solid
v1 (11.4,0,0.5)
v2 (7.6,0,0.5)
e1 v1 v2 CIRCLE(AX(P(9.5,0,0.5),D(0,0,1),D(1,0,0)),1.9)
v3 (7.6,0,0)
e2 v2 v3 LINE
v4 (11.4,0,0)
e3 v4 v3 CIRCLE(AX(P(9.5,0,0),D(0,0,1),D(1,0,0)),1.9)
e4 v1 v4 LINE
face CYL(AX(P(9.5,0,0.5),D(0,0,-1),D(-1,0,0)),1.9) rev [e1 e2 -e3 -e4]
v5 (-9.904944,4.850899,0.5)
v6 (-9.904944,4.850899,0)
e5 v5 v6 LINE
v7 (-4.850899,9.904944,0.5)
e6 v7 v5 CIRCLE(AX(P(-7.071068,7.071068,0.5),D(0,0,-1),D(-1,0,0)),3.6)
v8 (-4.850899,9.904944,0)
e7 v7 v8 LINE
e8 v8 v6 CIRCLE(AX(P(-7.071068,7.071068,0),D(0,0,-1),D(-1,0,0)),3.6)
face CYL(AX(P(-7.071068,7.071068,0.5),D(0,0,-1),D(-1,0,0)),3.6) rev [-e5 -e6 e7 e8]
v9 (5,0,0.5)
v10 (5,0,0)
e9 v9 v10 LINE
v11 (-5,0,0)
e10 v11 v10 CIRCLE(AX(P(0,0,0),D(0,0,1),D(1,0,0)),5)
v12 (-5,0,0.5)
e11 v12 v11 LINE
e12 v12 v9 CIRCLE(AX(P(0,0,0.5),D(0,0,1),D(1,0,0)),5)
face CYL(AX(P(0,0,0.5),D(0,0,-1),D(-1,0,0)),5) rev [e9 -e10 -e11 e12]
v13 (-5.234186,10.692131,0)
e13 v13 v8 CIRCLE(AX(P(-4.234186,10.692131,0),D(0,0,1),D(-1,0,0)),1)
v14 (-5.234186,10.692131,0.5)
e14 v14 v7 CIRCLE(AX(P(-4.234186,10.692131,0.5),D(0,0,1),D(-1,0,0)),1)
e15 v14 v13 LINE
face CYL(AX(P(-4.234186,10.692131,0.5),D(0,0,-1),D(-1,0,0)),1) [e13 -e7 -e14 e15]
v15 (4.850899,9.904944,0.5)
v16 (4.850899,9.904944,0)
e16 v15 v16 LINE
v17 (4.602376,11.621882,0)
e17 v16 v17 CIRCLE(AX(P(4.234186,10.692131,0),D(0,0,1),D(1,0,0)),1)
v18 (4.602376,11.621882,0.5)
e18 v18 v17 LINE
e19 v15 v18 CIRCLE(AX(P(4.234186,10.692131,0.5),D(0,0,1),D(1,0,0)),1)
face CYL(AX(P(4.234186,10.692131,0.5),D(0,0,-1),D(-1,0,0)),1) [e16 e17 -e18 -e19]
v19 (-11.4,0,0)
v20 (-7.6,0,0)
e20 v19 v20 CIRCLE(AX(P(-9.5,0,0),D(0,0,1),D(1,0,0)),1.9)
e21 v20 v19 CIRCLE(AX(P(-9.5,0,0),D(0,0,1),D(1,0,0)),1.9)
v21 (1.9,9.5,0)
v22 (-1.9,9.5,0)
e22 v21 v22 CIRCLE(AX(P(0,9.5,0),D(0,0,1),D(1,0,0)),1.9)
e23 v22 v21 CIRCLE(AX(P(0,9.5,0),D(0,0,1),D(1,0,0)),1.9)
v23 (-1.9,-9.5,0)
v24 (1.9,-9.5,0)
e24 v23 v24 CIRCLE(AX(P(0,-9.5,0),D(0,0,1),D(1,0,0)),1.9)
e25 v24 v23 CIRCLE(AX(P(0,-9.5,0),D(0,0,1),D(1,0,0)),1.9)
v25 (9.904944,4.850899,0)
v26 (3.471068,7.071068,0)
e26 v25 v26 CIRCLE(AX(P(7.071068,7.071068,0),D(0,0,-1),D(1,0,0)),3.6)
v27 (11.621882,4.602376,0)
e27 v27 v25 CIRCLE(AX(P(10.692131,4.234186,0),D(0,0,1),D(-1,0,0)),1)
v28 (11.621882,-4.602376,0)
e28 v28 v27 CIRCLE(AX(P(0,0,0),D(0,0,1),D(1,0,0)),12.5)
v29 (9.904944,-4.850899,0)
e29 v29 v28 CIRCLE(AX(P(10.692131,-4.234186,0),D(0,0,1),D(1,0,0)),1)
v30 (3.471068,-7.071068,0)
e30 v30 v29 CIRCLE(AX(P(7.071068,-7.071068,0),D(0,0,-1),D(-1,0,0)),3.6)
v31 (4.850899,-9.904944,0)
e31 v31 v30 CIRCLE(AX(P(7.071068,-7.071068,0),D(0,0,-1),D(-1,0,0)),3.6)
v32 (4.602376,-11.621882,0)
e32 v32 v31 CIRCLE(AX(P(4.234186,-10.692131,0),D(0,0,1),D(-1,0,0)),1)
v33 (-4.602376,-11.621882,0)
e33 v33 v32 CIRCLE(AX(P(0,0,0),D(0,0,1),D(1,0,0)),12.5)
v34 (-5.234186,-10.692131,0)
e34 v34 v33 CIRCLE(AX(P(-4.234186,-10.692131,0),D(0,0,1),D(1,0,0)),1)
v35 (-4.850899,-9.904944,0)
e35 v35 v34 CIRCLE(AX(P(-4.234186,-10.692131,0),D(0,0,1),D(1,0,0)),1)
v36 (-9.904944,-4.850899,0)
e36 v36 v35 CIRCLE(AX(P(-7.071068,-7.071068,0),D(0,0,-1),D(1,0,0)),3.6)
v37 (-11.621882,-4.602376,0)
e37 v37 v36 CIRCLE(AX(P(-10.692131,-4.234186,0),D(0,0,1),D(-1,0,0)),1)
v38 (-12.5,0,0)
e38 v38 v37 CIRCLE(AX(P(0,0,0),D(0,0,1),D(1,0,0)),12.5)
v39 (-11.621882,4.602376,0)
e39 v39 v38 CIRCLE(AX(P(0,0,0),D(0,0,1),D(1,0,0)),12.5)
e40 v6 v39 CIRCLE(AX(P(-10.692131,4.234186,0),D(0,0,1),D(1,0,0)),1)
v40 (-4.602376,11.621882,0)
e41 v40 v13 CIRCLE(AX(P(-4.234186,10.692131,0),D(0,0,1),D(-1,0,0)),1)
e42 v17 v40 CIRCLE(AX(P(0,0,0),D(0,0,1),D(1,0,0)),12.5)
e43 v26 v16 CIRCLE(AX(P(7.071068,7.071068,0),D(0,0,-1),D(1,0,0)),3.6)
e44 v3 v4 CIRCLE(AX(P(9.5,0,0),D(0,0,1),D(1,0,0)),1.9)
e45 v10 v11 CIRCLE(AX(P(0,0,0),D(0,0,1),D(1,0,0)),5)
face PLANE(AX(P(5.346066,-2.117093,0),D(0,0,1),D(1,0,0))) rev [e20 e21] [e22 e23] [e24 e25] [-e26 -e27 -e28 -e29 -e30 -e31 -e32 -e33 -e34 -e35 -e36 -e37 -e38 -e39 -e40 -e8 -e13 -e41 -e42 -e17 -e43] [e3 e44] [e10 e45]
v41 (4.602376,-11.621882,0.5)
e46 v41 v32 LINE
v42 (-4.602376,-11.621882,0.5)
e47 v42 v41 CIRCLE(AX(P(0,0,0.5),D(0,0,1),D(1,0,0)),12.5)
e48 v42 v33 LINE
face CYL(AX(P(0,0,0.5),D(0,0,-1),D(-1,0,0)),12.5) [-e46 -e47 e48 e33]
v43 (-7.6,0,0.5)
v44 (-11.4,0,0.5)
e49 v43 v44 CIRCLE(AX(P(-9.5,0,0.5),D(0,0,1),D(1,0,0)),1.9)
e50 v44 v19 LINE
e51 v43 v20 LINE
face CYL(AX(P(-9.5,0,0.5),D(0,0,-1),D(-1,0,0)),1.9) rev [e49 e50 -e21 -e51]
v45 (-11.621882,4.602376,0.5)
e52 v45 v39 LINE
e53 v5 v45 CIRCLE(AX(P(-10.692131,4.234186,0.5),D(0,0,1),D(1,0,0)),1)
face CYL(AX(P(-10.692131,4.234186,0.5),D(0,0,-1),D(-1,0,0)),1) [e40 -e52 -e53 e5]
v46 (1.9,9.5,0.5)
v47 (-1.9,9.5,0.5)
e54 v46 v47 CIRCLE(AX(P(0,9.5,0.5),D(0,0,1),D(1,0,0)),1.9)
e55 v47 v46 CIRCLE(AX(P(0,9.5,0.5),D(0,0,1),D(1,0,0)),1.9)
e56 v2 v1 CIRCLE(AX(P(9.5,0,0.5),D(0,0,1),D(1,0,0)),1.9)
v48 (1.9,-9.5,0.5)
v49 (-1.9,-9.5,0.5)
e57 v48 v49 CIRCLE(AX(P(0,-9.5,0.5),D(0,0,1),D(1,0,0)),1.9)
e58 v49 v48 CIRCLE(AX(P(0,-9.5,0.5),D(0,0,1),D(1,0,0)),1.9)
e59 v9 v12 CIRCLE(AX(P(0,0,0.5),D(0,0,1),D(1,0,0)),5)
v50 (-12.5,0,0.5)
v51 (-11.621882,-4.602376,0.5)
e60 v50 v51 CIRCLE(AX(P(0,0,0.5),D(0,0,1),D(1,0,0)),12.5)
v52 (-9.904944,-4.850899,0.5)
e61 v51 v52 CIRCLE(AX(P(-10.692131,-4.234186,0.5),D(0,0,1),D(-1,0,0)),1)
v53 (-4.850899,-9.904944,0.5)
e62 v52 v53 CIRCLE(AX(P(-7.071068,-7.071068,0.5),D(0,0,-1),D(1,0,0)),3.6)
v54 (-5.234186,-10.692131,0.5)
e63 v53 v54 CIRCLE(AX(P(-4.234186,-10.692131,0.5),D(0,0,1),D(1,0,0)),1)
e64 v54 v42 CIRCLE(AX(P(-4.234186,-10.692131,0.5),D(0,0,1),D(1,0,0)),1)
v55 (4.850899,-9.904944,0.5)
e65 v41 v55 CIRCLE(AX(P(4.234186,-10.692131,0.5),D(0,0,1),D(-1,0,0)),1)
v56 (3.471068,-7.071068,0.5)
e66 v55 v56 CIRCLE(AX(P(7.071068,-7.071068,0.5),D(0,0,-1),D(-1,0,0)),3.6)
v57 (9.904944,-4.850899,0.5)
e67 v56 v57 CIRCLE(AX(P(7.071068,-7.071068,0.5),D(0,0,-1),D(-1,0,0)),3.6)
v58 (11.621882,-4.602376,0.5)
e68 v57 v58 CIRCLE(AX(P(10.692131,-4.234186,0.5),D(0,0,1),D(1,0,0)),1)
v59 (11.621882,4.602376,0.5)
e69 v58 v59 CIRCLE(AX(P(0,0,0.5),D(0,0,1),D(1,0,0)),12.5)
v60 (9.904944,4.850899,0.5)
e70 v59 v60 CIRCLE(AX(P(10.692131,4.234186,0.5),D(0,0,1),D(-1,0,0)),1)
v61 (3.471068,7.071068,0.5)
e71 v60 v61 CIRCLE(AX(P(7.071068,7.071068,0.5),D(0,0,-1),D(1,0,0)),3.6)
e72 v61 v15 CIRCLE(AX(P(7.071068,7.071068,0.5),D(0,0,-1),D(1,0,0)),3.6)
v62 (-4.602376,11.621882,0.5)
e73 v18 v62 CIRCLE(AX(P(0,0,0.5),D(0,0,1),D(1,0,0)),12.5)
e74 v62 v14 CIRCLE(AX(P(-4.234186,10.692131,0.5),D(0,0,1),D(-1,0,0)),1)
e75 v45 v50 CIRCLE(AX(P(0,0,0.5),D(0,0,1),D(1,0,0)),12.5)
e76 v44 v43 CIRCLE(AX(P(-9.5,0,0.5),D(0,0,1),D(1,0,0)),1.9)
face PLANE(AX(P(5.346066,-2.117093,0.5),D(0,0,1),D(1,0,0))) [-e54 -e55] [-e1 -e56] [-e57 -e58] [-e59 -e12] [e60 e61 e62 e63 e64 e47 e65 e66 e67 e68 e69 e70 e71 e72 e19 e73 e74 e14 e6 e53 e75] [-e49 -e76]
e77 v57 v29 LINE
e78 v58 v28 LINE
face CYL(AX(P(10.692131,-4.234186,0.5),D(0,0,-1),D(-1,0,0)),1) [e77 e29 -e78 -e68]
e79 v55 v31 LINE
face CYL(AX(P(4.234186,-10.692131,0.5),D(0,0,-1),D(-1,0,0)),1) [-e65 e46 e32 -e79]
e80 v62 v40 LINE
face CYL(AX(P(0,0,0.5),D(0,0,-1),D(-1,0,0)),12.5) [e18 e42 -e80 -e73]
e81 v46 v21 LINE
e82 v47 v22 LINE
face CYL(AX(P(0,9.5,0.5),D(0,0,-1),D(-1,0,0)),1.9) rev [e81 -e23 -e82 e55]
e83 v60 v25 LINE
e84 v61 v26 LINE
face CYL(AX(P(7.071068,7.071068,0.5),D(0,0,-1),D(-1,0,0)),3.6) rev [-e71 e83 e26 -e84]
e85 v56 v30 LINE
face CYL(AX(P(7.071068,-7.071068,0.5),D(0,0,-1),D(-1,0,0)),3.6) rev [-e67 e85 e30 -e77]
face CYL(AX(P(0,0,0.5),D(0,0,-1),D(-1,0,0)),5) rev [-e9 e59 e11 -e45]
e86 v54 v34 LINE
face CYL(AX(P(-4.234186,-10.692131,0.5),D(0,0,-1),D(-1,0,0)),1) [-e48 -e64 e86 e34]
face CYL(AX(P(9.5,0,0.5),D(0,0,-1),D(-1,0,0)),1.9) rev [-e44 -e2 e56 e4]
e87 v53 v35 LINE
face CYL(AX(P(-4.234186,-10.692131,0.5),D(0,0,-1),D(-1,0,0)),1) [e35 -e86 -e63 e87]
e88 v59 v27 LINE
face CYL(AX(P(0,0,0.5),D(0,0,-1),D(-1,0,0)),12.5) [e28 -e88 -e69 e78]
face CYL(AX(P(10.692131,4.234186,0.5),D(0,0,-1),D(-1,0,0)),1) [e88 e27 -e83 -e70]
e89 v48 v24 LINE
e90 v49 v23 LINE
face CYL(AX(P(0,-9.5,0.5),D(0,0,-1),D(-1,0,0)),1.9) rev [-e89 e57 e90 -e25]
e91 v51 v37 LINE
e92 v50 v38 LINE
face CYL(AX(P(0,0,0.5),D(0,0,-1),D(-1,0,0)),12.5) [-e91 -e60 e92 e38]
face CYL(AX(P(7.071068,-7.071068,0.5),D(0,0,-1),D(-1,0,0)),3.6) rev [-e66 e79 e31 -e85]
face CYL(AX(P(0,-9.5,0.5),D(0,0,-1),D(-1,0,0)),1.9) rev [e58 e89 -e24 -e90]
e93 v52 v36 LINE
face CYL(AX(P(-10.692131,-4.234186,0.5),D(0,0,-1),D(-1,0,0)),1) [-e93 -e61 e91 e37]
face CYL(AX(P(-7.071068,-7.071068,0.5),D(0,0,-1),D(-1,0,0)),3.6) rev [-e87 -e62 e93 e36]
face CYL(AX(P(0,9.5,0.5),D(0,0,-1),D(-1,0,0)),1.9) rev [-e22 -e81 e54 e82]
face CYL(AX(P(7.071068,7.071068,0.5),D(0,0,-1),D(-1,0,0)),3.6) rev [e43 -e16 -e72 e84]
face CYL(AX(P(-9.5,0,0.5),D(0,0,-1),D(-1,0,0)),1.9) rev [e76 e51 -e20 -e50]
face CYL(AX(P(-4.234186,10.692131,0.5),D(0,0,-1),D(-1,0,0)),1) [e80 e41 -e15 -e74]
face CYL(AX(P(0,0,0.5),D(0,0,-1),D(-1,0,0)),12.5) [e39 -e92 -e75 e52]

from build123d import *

# Parameters (mm, degrees)
SKETCH1_R           = 5
SKETCH1_R_2         = 1.9
BOSS_EXTRUDE1_DEPTH = 0.5


with BuildPart() as part:
    # Sketch1 → Boss-Extrude1 (new body)
    with BuildSketch(Plane.XY):
        with BuildLine():
            ThreePointArc((-11.621881793, 4.602375864), (-12.5, 0), (-11.621881793, -4.602375864))
            ThreePointArc((-11.621881793, -4.602375864), (-10.835386311, -5.223871597), (-9.904943546, -4.850899277))
            ThreePointArc((-9.904943546, -4.850899277), (-4.5254834, -4.5254834), (-4.850899277, -9.904943546))
            ThreePointArc((-4.850899277, -9.904943546), (-5.223871597, -10.835386311), (-4.602375864, -11.621881793))
            ThreePointArc((-4.602375864, -11.621881793), (0, -12.5), (4.602375864, -11.621881793))
            ThreePointArc((4.602375864, -11.621881793), (5.223871597, -10.835386311), (4.850899277, -9.904943546))
            ThreePointArc((4.850899277, -9.904943546), (4.5254834, -4.5254834), (9.904943546, -4.850899277))
            ThreePointArc((9.904943546, -4.850899277), (10.835386311, -5.223871597), (11.621881793, -4.602375864))
            ThreePointArc((11.621881793, -4.602375864), (12.5, 0), (11.621881793, 4.602375864))
            ThreePointArc((11.621881793, 4.602375864), (10.835386311, 5.223871597), (9.904943546, 4.850899277))
            ThreePointArc((9.904943546, 4.850899277), (4.5254834, 4.5254834), (4.850899277, 9.904943546))
            ThreePointArc((4.850899277, 9.904943546), (5.223871597, 10.835386311), (4.602375864, 11.621881793))
            ThreePointArc((4.602375864, 11.621881793), (0, 12.5), (-4.602375864, 11.621881793))
            ThreePointArc((-4.602375864, 11.621881793), (-5.223871597, 10.835386311), (-4.850899277, 9.904943546))
            ThreePointArc((-4.850899277, 9.904943546), (-4.5254834, 4.5254834), (-9.904943546, 4.850899277))
            ThreePointArc((-9.904943546, 4.850899277), (-10.835386311, 5.223871597), (-11.621881793, 4.602375864))
        make_face()
        Circle(SKETCH1_R, mode=Mode.SUBTRACT)
        with Locations((0, 9.5)):
            Circle(SKETCH1_R_2, mode=Mode.SUBTRACT)
        with Locations((9.5, 0)):
            Circle(SKETCH1_R_2, mode=Mode.SUBTRACT)
        with Locations((0, -9.5)):
            Circle(SKETCH1_R_2, mode=Mode.SUBTRACT)
        with Locations((-9.5, 0)):
            Circle(SKETCH1_R_2, mode=Mode.SUBTRACT)
    extrude(amount=BOSS_EXTRUDE1_DEPTH)


solid = part.part
